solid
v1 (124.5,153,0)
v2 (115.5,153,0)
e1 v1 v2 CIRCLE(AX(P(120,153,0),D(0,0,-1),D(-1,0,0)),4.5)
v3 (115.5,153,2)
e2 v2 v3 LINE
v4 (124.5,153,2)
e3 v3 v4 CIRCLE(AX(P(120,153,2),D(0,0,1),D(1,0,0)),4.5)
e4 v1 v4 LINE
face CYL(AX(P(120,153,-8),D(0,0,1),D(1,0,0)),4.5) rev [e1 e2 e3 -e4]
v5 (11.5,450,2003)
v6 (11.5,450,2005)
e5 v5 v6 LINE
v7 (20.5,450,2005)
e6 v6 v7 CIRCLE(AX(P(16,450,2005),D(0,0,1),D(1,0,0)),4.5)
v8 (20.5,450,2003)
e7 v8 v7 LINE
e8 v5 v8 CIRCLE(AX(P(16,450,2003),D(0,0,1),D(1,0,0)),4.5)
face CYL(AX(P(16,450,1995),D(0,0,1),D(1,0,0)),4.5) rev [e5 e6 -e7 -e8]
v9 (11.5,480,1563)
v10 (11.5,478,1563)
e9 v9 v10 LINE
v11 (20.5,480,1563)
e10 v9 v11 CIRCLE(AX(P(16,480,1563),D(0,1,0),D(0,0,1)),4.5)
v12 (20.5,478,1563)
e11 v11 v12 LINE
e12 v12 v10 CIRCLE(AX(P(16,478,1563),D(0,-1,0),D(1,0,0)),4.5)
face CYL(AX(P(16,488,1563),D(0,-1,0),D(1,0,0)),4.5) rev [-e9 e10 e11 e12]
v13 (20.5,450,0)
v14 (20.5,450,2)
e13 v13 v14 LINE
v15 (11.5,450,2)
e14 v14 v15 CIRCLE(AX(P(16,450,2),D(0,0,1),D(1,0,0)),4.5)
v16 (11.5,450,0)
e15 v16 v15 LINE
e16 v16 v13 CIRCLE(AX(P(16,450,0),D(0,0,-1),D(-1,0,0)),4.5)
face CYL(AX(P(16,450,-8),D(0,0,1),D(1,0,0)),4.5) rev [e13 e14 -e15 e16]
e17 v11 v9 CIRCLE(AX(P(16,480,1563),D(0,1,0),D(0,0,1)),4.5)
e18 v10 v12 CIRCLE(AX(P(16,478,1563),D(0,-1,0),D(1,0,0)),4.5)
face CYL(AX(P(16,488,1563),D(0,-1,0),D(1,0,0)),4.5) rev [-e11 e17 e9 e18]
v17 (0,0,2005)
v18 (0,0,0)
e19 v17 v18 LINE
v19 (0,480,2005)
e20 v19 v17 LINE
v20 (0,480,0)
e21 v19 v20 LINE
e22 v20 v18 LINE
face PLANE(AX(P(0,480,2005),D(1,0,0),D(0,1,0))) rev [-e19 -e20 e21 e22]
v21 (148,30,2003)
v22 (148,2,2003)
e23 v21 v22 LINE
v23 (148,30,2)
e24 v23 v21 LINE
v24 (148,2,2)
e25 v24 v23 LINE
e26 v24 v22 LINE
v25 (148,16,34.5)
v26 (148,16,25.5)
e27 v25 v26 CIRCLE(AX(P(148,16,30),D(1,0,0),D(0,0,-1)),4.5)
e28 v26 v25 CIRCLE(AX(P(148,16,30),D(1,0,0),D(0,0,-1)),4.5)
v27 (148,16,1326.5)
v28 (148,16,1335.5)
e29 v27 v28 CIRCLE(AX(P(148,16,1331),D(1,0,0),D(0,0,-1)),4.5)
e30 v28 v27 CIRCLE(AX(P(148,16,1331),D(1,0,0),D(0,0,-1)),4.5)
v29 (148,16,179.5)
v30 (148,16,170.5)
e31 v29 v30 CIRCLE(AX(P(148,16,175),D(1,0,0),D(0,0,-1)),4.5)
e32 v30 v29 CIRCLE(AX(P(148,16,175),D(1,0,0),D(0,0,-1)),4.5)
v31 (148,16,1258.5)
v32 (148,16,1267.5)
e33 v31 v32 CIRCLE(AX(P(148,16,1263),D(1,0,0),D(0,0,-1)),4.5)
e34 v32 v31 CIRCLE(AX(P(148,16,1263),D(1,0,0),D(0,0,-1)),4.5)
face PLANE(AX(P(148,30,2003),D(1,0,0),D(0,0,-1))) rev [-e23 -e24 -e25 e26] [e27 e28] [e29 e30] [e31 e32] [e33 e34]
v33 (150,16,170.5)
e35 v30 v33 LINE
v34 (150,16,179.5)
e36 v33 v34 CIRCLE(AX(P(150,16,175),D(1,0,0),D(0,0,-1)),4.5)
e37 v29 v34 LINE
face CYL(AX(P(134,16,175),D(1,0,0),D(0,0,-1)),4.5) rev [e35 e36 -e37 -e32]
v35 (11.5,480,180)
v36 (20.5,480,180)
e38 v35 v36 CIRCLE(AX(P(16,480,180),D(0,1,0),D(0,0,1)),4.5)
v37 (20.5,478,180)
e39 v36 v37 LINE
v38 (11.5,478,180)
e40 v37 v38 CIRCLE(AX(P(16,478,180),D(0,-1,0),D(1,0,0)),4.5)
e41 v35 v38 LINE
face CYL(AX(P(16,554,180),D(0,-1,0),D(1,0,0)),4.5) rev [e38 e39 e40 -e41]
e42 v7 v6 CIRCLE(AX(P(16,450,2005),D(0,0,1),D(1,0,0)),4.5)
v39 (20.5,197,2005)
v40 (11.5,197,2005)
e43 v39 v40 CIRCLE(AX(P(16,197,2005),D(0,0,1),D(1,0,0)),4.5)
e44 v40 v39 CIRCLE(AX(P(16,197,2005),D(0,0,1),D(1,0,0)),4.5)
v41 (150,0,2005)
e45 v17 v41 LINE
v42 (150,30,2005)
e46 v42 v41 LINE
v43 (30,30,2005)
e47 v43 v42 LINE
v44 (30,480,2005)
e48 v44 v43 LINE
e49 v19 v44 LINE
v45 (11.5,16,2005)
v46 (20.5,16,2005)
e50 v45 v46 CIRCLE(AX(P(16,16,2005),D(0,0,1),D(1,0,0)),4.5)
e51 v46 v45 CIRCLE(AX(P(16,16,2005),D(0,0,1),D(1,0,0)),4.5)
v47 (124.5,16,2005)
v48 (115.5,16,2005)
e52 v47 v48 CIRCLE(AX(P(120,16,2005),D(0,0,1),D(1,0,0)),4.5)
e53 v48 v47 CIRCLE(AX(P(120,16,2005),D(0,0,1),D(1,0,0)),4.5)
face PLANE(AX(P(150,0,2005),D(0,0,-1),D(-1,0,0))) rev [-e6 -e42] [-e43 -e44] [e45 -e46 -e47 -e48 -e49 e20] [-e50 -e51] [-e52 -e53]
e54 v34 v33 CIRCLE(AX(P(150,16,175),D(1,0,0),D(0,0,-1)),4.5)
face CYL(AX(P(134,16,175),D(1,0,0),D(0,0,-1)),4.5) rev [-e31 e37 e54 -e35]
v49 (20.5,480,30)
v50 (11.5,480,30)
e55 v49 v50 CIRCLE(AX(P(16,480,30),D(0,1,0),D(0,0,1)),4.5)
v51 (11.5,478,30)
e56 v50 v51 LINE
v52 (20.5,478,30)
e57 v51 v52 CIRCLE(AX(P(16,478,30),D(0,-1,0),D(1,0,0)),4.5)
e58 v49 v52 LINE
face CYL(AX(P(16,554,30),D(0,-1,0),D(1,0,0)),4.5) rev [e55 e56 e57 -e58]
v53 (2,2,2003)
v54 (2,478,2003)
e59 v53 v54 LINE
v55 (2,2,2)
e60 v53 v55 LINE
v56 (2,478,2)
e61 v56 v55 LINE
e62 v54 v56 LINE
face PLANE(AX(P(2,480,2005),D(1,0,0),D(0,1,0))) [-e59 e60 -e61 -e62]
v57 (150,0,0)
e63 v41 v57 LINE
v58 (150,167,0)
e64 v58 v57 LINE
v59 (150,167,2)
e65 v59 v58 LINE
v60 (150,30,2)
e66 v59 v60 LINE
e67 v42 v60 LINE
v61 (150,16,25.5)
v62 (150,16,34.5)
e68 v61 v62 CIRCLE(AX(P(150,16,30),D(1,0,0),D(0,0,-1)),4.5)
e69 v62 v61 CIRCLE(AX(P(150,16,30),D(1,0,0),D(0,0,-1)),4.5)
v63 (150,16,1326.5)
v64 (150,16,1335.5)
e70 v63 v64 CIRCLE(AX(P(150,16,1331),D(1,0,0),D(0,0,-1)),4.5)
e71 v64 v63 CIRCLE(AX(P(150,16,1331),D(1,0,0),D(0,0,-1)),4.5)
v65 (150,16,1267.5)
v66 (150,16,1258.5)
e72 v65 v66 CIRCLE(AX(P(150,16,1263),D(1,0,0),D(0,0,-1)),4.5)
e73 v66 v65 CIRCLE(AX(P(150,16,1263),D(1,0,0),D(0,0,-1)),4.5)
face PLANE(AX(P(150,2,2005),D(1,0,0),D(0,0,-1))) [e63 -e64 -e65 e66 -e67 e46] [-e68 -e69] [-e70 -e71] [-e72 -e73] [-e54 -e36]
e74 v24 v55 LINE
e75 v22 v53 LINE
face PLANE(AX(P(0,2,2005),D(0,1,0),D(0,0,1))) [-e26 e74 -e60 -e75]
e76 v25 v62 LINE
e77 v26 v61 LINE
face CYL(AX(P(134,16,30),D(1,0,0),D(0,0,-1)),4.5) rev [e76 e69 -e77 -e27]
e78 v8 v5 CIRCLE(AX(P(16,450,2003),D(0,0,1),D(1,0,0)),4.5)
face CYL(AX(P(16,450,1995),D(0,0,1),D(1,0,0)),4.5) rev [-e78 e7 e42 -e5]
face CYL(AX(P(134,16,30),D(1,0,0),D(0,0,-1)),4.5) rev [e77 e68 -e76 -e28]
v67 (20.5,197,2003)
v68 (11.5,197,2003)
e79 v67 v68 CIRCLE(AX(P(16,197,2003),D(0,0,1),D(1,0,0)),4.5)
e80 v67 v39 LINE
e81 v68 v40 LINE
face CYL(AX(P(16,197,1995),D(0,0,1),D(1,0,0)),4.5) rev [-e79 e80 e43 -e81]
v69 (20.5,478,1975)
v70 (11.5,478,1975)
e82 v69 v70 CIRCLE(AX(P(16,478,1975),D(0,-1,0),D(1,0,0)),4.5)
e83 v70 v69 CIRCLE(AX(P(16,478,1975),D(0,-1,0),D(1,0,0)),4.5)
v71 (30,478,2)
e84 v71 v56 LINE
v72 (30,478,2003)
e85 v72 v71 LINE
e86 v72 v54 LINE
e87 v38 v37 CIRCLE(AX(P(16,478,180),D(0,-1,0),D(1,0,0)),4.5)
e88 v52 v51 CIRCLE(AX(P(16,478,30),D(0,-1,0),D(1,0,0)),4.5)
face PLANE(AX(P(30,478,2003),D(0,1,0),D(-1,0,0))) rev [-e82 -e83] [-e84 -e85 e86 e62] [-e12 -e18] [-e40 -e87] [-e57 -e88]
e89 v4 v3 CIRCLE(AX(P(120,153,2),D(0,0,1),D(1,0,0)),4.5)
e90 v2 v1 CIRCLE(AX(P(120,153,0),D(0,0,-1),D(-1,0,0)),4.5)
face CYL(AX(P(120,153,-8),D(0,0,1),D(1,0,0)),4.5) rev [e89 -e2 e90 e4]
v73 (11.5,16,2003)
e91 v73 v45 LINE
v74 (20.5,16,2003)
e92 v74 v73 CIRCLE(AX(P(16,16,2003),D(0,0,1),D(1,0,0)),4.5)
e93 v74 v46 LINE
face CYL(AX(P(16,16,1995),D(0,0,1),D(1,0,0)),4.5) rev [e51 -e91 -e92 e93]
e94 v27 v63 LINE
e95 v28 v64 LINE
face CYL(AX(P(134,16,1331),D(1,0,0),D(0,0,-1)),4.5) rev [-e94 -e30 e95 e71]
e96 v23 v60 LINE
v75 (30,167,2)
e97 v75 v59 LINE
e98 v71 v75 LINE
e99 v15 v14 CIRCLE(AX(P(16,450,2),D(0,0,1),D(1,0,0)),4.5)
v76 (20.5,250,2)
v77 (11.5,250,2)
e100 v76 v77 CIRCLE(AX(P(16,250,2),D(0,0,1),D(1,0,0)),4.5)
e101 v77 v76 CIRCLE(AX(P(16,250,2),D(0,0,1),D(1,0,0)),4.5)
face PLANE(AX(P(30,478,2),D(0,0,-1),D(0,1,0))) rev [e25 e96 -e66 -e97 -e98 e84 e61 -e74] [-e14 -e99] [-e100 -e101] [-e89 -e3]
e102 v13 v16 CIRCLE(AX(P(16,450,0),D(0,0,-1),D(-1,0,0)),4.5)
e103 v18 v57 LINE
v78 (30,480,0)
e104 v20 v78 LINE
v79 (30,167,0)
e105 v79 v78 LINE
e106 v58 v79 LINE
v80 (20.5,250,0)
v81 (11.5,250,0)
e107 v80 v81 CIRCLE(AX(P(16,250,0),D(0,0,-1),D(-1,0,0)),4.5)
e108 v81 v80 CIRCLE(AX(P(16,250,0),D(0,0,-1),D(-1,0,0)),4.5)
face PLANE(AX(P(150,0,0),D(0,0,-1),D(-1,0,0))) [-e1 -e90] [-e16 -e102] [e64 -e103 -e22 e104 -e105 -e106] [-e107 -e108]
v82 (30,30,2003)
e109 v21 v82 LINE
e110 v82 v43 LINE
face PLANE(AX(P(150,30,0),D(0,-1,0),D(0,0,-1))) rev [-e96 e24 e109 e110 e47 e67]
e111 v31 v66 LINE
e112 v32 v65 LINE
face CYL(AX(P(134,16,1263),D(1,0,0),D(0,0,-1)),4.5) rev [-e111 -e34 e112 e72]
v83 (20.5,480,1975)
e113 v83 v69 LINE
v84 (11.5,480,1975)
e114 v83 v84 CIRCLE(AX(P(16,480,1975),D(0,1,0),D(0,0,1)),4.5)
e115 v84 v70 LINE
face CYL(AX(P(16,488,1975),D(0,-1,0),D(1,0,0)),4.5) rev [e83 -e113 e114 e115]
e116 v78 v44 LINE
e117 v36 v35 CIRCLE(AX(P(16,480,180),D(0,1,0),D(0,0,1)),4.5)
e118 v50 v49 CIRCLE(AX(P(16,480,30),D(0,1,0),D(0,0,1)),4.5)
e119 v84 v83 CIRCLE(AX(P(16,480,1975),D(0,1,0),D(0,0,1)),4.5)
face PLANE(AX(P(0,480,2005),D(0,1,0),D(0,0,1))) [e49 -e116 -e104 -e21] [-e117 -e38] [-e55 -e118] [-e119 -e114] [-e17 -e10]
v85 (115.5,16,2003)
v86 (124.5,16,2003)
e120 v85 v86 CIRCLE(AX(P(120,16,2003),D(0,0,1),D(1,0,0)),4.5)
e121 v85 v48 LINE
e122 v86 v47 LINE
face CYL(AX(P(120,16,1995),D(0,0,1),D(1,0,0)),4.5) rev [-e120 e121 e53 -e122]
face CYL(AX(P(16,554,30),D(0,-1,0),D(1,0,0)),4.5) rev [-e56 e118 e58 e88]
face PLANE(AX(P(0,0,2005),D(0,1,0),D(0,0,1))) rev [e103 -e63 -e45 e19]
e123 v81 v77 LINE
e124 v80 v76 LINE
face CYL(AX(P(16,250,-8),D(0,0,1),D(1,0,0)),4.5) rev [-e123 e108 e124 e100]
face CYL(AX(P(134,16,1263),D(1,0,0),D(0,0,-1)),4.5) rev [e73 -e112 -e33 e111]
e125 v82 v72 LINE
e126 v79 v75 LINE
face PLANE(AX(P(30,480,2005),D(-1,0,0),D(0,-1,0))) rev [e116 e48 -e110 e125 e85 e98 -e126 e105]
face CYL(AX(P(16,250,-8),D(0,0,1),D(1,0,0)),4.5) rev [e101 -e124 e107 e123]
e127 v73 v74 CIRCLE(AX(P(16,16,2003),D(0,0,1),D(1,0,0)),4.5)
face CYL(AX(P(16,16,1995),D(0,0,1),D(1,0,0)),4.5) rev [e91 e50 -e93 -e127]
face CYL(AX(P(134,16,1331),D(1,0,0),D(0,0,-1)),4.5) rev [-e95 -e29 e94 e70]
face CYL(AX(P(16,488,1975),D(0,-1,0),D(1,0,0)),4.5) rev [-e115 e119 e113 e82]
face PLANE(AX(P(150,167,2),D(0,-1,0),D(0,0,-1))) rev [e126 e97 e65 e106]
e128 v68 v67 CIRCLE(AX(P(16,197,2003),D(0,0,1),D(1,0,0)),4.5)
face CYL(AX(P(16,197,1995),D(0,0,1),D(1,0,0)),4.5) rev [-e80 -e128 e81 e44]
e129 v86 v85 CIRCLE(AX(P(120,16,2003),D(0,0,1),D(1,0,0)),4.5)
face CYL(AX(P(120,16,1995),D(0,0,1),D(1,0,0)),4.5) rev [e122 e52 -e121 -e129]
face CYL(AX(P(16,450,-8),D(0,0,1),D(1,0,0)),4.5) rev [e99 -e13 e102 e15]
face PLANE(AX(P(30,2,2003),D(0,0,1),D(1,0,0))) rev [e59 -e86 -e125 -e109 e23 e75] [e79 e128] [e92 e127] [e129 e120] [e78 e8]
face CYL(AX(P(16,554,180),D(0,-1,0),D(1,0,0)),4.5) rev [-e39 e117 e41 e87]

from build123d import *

# Parameters (mm, degrees)
EXTRUDE_1_DEPTH     = 2005
EXTRUDE_1_2_DEPTH   = 28
EXTRUDE_2_DEPTH     = 28
SKETCH_5_W          = 120
SKETCH_5_H          = 2
EXTRUDE_3_DEPTH     = 165
SKETCH_7_R          = 4.5
CUT_EXTRUDE_2_DEPTH = 10
SKETCH_8_R          = 4.5
CUT_EXTRUDE_3_DEPTH = 76
SKETCH_9_R          = 4.5
CUT_EXTRUDE_4_DEPTH = 10
SKETCH_10_R         = 4.5
CUT_EXTRUDE_5_DEPTH = 10
SKETCH_11_R         = 4.5
CUT_EXTRUDE_6_DEPTH = 16


with BuildPart() as part:
    # 草图1 → Extrude 1 (new body)
    with BuildSketch(Plane.XY):
        Polygon((0, 480), (0, 0), (150, 0), (150, 2), (2, 2), (2, 480), align=None)
    extrude(amount=EXTRUDE_1_DEPTH)

    # 草图3 → Extrude 1 2 (add)
    with BuildSketch(Plane(origin=(2, 0, 0), x_dir=(0, 0, -1), z_dir=(1, 0, 0))):
        Polygon((-2003, 2), (-2003, 478), (-2, 478), (-2, 2), (0, 2), (0, 480), (-2005, 480), (-2005, 2), align=None)
    extrude(amount=EXTRUDE_1_2_DEPTH)

    # 草图4 → 凸台-拉伸2 (add)
    with BuildSketch(Plane(origin=(0, 2, 0), x_dir=(1, 0, 0), z_dir=(0, 1, 0))):
        Polygon((148, -2003), (148, 0), (150, 0), (150, -2005), (30, -2005), (30, -2003), align=None)
    extrude(amount=EXTRUDE_2_DEPTH)

    # 草图5 → 凸台-拉伸3 (add)
    with BuildSketch(Plane(origin=(0, 2, 0), x_dir=(1, 0, 0), z_dir=(0, 1, 0))):
        with Locations((90, -1)):
            Rectangle(SKETCH_5_W, SKETCH_5_H)
    extrude(amount=EXTRUDE_3_DEPTH)

    # 草图7 → 切除-拉伸2 (cut)
    with BuildSketch(Plane.XY.offset(2)):
        with Locations((120, 153)):
            Circle(SKETCH_7_R)
        with Locations((16, 450)):
            Circle(SKETCH_7_R)
        with Locations((16, 250)):
            Circle(SKETCH_7_R)
    extrude(amount=-CUT_EXTRUDE_2_DEPTH, mode=Mode.SUBTRACT)

    # 草图8 → 切除-拉伸3 (cut)
    with BuildSketch(Plane.XZ.offset(-478)):
        with Locations((16, 30)):
            Circle(SKETCH_8_R)
        with Locations((16, 180)):
            Circle(SKETCH_8_R)
    extrude(amount=-CUT_EXTRUDE_3_DEPTH, mode=Mode.SUBTRACT)

    # 草图9 → 切除-拉伸4 (cut)
    with BuildSketch(Plane.XZ.offset(-478)):
        with Locations((16, 1975)):
            Circle(SKETCH_9_R)
        with Locations((16, 1563)):
            Circle(SKETCH_9_R)
    extrude(amount=-CUT_EXTRUDE_4_DEPTH, mode=Mode.SUBTRACT)

    # 草图10 → 切除-拉伸5 (cut)
    with BuildSketch(Plane.XY.offset(2005)):
        with Locations((16, 450)):
            Circle(SKETCH_10_R)
        with Locations((16, 197)):
            Circle(SKETCH_10_R)
        with Locations((16, 16)):
            Circle(SKETCH_10_R)
        with Locations((120, 16)):
            Circle(SKETCH_10_R)
    extrude(amount=-CUT_EXTRUDE_5_DEPTH, mode=Mode.SUBTRACT)

    # 草图11 → 切除-拉伸6 (cut)
    with BuildSketch(Plane(origin=(150, 0, 0), x_dir=(0, 0, -1), z_dir=(1, 0, 0))):
        with Locations((-30, 16)):
            Circle(SKETCH_11_R)
        with Locations((-175, 16)):
            Circle(SKETCH_11_R)
        with Locations((-1331, 16)):
            Circle(SKETCH_11_R)
        with Locations((-1263, 16)):
            Circle(SKETCH_11_R)
    extrude(amount=-CUT_EXTRUDE_6_DEPTH, mode=Mode.SUBTRACT)


solid = part.part
